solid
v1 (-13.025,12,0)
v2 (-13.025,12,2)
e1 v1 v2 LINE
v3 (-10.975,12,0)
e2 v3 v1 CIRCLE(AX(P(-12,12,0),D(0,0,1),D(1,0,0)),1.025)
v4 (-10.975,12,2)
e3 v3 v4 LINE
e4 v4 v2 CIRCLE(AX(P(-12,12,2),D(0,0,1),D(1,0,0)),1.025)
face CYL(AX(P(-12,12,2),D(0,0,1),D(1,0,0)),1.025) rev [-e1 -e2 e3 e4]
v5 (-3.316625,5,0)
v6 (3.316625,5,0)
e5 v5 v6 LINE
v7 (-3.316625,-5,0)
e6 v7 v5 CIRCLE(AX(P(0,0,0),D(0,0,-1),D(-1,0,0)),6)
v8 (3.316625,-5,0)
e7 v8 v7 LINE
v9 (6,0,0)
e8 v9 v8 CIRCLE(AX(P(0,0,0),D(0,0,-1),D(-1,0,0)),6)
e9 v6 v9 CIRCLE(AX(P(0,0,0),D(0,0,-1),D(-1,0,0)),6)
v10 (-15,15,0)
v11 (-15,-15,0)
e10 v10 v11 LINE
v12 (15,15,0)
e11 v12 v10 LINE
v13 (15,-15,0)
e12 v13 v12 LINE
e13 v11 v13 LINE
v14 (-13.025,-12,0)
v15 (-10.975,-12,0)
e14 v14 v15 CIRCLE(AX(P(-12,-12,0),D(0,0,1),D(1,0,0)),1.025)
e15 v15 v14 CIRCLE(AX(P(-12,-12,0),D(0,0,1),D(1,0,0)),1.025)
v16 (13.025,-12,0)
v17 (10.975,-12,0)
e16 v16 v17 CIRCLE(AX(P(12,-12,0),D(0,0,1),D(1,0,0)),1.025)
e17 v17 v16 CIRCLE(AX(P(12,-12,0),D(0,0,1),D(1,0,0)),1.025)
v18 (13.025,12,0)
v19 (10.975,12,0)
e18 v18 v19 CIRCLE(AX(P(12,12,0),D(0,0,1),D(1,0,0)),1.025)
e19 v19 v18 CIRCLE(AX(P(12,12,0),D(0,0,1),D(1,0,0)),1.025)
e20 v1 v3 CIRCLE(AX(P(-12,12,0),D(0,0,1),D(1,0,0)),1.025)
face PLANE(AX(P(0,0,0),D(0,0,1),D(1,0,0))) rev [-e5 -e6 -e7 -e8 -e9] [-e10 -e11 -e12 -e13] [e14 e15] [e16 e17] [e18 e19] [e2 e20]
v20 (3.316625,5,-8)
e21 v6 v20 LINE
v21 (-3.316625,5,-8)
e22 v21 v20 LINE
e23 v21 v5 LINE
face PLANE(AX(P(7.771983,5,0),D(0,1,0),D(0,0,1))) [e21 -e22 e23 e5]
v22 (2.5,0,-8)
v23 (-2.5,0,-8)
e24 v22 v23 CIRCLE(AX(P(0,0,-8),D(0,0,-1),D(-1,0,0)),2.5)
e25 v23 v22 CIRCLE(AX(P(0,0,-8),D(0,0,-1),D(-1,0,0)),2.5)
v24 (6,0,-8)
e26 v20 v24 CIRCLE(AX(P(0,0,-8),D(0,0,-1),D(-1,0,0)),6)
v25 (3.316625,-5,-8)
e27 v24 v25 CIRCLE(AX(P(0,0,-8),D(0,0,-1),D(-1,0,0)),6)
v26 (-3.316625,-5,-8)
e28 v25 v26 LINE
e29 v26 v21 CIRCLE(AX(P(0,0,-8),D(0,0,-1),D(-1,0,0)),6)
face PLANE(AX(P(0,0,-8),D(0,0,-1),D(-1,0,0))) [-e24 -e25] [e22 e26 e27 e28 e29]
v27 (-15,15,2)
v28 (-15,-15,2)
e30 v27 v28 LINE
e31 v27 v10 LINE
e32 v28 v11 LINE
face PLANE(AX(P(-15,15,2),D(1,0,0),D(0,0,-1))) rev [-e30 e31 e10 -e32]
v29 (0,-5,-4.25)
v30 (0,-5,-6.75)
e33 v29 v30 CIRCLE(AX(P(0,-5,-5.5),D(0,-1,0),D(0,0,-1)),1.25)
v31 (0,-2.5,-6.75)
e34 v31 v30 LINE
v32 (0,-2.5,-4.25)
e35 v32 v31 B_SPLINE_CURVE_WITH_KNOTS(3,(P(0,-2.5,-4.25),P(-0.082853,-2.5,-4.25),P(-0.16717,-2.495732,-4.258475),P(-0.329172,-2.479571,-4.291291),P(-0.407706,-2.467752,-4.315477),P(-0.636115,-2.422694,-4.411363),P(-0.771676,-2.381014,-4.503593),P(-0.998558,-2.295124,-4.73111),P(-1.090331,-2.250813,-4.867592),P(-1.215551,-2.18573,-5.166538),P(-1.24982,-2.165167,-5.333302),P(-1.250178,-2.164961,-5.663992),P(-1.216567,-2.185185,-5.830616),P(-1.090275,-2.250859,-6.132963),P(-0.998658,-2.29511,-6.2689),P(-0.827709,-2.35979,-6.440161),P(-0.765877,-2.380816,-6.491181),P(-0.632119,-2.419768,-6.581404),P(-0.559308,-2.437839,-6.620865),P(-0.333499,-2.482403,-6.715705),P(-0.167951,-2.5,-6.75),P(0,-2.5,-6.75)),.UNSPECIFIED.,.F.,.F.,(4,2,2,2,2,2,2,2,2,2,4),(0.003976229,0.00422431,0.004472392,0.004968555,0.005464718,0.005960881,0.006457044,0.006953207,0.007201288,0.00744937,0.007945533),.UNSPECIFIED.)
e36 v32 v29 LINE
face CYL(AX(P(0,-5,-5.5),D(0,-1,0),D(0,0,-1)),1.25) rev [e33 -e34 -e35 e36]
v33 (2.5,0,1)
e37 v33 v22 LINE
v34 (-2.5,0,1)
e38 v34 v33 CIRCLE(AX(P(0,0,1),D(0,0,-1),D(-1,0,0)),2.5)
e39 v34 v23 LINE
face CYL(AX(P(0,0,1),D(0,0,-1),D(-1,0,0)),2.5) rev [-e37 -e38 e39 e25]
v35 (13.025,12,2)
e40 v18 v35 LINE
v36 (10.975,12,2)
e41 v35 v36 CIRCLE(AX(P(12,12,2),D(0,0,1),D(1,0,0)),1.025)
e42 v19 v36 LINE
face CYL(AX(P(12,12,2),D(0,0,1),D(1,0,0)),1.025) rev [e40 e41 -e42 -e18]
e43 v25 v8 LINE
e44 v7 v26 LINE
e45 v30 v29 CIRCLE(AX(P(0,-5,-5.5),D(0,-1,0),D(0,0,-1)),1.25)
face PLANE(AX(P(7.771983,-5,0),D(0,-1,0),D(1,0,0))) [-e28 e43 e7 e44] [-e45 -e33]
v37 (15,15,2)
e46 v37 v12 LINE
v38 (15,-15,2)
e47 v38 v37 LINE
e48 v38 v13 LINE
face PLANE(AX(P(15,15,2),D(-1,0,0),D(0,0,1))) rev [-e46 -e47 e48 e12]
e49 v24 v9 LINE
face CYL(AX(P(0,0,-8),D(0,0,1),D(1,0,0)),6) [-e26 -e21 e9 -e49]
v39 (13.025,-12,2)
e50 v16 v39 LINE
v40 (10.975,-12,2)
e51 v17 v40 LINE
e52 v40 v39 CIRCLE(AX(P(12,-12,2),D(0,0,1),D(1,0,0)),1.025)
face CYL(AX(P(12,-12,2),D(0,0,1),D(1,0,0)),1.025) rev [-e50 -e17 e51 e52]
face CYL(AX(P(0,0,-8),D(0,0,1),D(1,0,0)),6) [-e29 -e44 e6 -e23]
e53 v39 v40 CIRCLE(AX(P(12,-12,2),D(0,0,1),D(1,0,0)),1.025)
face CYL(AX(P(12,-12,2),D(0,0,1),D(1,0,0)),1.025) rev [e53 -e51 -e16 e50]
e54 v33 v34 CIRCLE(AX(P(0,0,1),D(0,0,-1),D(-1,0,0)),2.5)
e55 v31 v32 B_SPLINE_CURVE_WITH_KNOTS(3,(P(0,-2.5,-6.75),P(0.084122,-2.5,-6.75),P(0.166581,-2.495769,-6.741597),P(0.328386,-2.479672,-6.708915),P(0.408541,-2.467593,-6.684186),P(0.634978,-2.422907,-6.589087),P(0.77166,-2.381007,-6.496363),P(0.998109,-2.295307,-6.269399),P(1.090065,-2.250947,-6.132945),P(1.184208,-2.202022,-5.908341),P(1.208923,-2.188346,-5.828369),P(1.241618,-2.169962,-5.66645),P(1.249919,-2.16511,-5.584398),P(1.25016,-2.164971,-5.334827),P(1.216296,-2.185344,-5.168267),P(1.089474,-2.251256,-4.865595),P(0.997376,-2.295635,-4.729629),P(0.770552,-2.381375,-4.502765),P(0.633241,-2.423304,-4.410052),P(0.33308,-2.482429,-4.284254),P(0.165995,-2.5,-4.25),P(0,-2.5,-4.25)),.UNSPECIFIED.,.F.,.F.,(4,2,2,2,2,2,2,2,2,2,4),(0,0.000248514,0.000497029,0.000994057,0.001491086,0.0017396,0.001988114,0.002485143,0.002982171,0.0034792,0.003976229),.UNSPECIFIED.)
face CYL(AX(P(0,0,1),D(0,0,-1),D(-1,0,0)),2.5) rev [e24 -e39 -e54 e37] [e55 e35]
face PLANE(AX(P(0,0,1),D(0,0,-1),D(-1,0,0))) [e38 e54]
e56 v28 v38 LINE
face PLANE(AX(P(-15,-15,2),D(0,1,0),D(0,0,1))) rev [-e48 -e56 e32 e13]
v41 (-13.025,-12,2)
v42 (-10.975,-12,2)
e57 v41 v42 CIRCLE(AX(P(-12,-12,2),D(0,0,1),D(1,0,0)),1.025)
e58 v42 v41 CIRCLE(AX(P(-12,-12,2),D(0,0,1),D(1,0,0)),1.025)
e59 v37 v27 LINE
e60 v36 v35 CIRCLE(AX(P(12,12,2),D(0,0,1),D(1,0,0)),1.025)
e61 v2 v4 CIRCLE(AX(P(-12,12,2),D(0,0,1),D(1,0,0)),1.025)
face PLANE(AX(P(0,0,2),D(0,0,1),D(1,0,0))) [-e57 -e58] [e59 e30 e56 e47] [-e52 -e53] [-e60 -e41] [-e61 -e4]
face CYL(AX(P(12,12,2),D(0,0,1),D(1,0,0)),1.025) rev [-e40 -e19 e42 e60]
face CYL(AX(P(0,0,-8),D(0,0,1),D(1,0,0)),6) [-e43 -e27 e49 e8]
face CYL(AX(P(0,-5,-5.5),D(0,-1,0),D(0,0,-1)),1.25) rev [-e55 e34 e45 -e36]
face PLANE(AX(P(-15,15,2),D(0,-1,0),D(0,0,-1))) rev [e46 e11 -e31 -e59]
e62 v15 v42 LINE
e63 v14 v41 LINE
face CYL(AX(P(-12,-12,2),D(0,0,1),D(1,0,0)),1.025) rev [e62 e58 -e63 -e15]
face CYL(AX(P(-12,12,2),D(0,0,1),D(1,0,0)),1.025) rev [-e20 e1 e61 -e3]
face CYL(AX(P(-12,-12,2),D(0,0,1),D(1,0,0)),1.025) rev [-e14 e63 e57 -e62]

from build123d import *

# Parameters (mm, degrees)
SKETCH1_W               = 30
SKETCH1_H               = 30
BOSS_EXTRUDE1_DEPTH     = 2
SKETCH2_R               = 6
BOSS_EXTRUDE2_DEPTH     = 8
SKETCH4_R               = 0.5
CUT_EXTRUDE1_DEPTH      = 10
SKETCH6_R               = 2.5
CUT_EXTRUDE3_DEPTH      = 9
CUT_EXTRUDE4_DEPTH      = 0.1
CUT_EXTRUDE4_DEPTH_BACK = 4
SKETCH7_R               = 0.5
SKETCH8_OUTSIDE_W       = 40.718
SKETCH8_OUTSIDE_H       = 40.718
SKETCH8_OUTSIDE_W_2     = 15.543966854
SKETCH8_OUTSIDE_H_2     = 10
CUT_EXTRUDE5_DEPTH      = 8
M3_TAPPED_HOLE1_D       = 2.5
M3_TAPPED_HOLE1_DEPTH   = 3
M3_TAPPED_HOLE1_TIP     = 0.751075774
M2_5_TAPPED_HOLE1_D     = 2.05


with BuildPart() as part:
    # Sketch1 → Boss-Extrude1 (new body)
    with BuildSketch(Plane.XY):
        Rectangle(SKETCH1_W, SKETCH1_H)
    extrude(amount=BOSS_EXTRUDE1_DEPTH)

    # Sketch2 → Boss-Extrude2 (add)
    with BuildSketch(Plane(origin=(0, 0, 0), x_dir=(-1, 0, 0), z_dir=(0, 0, -1))):
        Circle(SKETCH2_R)
    extrude(amount=BOSS_EXTRUDE2_DEPTH)

    # Sketch4 → Cut-Extrude1 (cut)
    with BuildSketch(Plane.XY.offset(2)):
        with Locations((-12, 12)):
            Circle(SKETCH4_R)
        with Locations((12, 12)):
            Circle(SKETCH4_R)
        with Locations((12, -12)):
            Circle(SKETCH4_R)
        with Locations((-12, -12)):
            Circle(SKETCH4_R)
    extrude(amount=-CUT_EXTRUDE1_DEPTH, mode=Mode.SUBTRACT)

    # Sketch6 → Cut-Extrude3 (cut)
    with BuildSketch(Plane(origin=(0, 0, -8), x_dir=(-1, 0, 0), z_dir=(0, 0, -1))):
        Circle(SKETCH6_R)
    extrude(amount=-CUT_EXTRUDE3_DEPTH, mode=Mode.SUBTRACT)

    # Sketch7 → Cut-Extrude4 (cut, two sides: drawn at the far end of the back side and taken through both)
    with BuildSketch(Plane(origin=(0, 0, 0), x_dir=(1, 0, 0), z_dir=(0, 1, 0)).offset(-CUT_EXTRUDE4_DEPTH_BACK)):
        with Locations(Location((0, 5.5, 0), (0, 0, 270))):
            Circle(SKETCH7_R)
    extrude(amount=CUT_EXTRUDE4_DEPTH + CUT_EXTRUDE4_DEPTH_BACK, mode=Mode.SUBTRACT)

    # Sketch8 outside → Cut-Extrude5 (cut)
    with BuildSketch(Plane(origin=(0, 0, -8), x_dir=(-1, 0, 0), z_dir=(0, 0, -1))):
        Rectangle(SKETCH8_OUTSIDE_W, SKETCH8_OUTSIDE_H)
        Rectangle(SKETCH8_OUTSIDE_W_2, SKETCH8_OUTSIDE_H_2, mode=Mode.SUBTRACT)
    extrude(amount=-CUT_EXTRUDE5_DEPTH, mode=Mode.SUBTRACT)

    # M3 Tapped Hole1
    with Locations(Plane(origin=(0, -5, 0), x_dir=(-1, 0, 0), z_dir=(0, -1, 0))):
        with Locations((0, 5.5)):
            Hole(M3_TAPPED_HOLE1_D / 2, depth=M3_TAPPED_HOLE1_DEPTH)
            with Locations((0, 0, -(M3_TAPPED_HOLE1_DEPTH + M3_TAPPED_HOLE1_TIP / 2))):  # 118° drill point
                Cone(0, M3_TAPPED_HOLE1_D / 2, M3_TAPPED_HOLE1_TIP, mode=Mode.SUBTRACT)

    # M2.5 Tapped Hole1 (through all)
    with Locations(Plane.XY.offset(2)):
        with Locations((12, 12), (12, -12), (-12, -12), (-12, 12)):
            Hole(M2_5_TAPPED_HOLE1_D / 2)


solid = part.part
